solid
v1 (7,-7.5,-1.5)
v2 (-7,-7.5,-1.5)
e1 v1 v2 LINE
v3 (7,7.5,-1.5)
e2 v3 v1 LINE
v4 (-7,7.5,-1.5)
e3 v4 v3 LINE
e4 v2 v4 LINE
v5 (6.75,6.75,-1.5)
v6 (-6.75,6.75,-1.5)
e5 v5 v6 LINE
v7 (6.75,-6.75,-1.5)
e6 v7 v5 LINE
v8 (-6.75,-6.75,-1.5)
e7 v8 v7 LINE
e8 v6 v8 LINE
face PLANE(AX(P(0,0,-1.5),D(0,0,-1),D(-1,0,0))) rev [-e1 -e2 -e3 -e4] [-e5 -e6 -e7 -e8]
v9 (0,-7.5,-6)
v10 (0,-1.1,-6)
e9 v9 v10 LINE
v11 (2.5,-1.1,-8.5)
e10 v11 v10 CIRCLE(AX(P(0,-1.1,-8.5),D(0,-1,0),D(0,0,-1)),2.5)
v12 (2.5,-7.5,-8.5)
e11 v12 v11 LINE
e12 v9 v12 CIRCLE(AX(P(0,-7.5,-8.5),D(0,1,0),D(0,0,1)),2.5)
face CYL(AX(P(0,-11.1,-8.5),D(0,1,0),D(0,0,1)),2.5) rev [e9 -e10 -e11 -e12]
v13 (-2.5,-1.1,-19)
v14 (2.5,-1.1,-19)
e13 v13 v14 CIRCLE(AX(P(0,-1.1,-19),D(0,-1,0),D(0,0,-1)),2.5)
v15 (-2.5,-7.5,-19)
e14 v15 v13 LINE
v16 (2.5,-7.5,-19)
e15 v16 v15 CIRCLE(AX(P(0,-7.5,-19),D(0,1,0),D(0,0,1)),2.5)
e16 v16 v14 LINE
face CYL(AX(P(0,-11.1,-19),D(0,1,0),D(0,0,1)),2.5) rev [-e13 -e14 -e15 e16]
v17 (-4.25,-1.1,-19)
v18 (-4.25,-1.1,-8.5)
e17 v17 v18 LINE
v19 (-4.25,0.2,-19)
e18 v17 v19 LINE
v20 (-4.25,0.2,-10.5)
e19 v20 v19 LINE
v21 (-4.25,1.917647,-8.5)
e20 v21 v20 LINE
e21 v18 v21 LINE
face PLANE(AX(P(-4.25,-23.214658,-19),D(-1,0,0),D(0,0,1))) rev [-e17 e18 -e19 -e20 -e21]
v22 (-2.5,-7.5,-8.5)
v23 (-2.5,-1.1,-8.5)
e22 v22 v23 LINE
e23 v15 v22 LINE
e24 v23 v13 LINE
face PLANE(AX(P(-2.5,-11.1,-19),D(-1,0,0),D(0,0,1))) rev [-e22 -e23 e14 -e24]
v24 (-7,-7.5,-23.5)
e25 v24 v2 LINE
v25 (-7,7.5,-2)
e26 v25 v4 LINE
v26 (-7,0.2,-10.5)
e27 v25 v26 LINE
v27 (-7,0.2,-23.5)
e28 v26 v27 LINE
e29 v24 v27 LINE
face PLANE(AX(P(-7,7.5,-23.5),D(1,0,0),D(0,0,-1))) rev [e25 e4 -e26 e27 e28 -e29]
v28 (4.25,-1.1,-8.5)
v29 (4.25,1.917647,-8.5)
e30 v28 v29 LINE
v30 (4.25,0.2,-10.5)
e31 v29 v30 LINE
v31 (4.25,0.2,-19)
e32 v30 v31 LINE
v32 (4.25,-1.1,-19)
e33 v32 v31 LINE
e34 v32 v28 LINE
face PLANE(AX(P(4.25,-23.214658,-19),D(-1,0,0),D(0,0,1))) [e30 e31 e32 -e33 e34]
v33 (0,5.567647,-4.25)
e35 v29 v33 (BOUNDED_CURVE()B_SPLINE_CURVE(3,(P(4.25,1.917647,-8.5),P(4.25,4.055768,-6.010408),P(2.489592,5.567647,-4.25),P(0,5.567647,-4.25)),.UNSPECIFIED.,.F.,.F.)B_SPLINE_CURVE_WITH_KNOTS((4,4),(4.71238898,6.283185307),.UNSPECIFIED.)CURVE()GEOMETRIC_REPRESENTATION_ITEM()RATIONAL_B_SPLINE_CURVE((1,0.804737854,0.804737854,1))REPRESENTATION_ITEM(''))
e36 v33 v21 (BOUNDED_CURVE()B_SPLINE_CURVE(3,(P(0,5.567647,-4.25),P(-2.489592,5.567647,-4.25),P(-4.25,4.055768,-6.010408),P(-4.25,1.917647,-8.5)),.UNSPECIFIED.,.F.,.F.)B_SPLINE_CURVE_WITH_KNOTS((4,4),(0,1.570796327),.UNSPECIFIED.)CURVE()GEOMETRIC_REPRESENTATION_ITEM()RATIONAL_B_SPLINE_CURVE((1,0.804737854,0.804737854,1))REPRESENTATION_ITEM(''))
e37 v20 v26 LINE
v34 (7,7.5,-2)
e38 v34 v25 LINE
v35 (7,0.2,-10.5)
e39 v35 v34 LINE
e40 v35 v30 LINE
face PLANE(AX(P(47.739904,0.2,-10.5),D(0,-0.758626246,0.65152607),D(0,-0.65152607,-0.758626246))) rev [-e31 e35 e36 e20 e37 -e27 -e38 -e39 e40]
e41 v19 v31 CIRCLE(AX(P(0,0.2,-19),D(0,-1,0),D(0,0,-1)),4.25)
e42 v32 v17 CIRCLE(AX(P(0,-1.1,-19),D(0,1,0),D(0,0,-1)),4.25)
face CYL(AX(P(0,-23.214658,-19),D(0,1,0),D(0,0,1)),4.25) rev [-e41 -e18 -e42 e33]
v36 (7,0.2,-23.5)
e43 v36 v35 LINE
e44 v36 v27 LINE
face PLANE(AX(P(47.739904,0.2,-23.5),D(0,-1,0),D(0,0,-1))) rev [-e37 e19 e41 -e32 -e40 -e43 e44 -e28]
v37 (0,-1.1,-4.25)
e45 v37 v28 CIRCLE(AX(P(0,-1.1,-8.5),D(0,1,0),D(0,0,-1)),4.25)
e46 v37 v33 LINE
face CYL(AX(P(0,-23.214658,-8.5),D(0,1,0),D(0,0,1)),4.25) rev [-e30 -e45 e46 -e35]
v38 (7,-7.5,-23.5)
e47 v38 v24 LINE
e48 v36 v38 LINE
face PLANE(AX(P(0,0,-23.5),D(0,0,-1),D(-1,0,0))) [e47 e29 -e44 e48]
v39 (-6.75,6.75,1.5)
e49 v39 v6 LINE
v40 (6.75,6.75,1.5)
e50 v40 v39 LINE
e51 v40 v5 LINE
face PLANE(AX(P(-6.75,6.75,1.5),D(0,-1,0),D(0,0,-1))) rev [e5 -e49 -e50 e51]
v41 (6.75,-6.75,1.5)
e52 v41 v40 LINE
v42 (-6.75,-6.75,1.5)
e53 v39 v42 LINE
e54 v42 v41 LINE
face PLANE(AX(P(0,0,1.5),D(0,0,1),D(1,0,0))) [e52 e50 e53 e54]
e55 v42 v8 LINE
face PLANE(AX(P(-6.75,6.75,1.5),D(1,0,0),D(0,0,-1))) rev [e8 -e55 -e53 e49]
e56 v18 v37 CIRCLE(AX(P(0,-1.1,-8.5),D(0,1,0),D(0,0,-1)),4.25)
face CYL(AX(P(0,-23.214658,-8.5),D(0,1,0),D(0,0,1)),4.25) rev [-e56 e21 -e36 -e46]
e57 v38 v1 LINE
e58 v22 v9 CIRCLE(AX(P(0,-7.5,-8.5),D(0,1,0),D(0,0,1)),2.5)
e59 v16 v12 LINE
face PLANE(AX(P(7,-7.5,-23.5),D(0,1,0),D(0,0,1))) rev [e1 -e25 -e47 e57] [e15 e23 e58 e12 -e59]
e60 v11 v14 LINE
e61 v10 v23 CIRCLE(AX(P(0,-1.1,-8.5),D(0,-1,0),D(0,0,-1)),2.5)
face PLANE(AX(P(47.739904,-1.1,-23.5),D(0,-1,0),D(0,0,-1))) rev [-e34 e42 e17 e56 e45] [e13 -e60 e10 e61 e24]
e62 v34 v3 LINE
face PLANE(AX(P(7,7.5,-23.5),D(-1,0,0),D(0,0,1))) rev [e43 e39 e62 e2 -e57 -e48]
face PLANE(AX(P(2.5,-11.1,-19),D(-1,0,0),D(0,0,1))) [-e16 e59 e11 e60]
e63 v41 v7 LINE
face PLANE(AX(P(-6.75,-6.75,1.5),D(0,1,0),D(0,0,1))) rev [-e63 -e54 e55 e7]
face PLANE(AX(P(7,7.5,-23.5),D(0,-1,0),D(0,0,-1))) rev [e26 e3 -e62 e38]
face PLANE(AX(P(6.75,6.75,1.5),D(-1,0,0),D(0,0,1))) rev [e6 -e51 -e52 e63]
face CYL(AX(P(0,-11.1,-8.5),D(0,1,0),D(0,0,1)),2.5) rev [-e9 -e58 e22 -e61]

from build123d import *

# Parameters (mm, degrees)
SKETCH1_W               = 13.5
SKETCH1_H               = 13.5
BOSS_EXTRUDE1_DEPTH     = 1.5
SKETCH2_W               = 14
SKETCH2_H               = 15
BOSS_EXTRUDE2_DEPTH     = 22
CUT_EXTRUDE2_DEPTH      = 29.363709207
CUT_EXTRUDE2_DEPTH_BACK = 29.363709207
CUT_EXTRUDE3_DEPTH      = 8.6
CUT_EXTRUDE4_DEPTH      = 11.3


with BuildPart() as part:
    # Sketch1 → Boss-Extrude1 (new, symmetric)
    with BuildSketch(Plane.XY):
        Rectangle(SKETCH1_W, SKETCH1_H)
    extrude(amount=BOSS_EXTRUDE1_DEPTH, both=True)

    # Sketch2 → Boss-Extrude2 (add)
    with BuildSketch(Plane(origin=(0, 0, -1.5), x_dir=(-1, 0, 0), z_dir=(0, 0, -1))):
        Rectangle(SKETCH2_W, SKETCH2_H)
    extrude(amount=BOSS_EXTRUDE2_DEPTH)

    # Sketch3 → Cut-Extrude2 (cut, two sides: drawn at the far end of the back side and taken through both)
    with BuildSketch(Plane(origin=(7, 0, 0), x_dir=(0, 0, -1), z_dir=(1, 0, 0)).offset(-CUT_EXTRUDE2_DEPTH_BACK)):
        Polygon((85.930906916, 0.2), (23.5, 0.2), (10.5, 0.2), (2, 7.5), (-45.361724521, 48.175363412), (-2.507621852, 165.452805564), (128.785009585, 117.477442152), align=None)
    extrude(amount=CUT_EXTRUDE2_DEPTH + CUT_EXTRUDE2_DEPTH_BACK, mode=Mode.SUBTRACT)

    # Sketch5 → Cut-Extrude3 (cut)
    with BuildSketch(Plane(origin=(0, 7.5, 0), x_dir=(1, 0, 0), z_dir=(0, 1, 0))):
        with BuildLine():
            Line((-4.25, 19), (-4.25, 8.5))
            ThreePointArc((-4.25, 8.5), (0, 4.25), (4.25, 8.5))
            Line((4.25, 8.5), (4.25, 19))
            ThreePointArc((4.25, 19), (0, 23.25), (-4.25, 19))
        make_face()
    extrude(amount=-CUT_EXTRUDE3_DEPTH, mode=Mode.SUBTRACT)

    # Sketch4 → Cut-Extrude4 (cut)
    with BuildSketch(Plane(origin=(0, 0.2, 0), x_dir=(1, 0, 0), z_dir=(0, 1, 0))):
        with BuildLine():
            Line((2.5, 19), (2.5, 8.5))
            ThreePointArc((2.5, 8.5), (0, 6), (-2.5, 8.5))
            Line((-2.5, 8.5), (-2.5, 19))
            ThreePointArc((-2.5, 19), (0, 21.5), (2.5, 19))
        make_face()
    extrude(amount=-CUT_EXTRUDE4_DEPTH, mode=Mode.SUBTRACT)


solid = part.part
